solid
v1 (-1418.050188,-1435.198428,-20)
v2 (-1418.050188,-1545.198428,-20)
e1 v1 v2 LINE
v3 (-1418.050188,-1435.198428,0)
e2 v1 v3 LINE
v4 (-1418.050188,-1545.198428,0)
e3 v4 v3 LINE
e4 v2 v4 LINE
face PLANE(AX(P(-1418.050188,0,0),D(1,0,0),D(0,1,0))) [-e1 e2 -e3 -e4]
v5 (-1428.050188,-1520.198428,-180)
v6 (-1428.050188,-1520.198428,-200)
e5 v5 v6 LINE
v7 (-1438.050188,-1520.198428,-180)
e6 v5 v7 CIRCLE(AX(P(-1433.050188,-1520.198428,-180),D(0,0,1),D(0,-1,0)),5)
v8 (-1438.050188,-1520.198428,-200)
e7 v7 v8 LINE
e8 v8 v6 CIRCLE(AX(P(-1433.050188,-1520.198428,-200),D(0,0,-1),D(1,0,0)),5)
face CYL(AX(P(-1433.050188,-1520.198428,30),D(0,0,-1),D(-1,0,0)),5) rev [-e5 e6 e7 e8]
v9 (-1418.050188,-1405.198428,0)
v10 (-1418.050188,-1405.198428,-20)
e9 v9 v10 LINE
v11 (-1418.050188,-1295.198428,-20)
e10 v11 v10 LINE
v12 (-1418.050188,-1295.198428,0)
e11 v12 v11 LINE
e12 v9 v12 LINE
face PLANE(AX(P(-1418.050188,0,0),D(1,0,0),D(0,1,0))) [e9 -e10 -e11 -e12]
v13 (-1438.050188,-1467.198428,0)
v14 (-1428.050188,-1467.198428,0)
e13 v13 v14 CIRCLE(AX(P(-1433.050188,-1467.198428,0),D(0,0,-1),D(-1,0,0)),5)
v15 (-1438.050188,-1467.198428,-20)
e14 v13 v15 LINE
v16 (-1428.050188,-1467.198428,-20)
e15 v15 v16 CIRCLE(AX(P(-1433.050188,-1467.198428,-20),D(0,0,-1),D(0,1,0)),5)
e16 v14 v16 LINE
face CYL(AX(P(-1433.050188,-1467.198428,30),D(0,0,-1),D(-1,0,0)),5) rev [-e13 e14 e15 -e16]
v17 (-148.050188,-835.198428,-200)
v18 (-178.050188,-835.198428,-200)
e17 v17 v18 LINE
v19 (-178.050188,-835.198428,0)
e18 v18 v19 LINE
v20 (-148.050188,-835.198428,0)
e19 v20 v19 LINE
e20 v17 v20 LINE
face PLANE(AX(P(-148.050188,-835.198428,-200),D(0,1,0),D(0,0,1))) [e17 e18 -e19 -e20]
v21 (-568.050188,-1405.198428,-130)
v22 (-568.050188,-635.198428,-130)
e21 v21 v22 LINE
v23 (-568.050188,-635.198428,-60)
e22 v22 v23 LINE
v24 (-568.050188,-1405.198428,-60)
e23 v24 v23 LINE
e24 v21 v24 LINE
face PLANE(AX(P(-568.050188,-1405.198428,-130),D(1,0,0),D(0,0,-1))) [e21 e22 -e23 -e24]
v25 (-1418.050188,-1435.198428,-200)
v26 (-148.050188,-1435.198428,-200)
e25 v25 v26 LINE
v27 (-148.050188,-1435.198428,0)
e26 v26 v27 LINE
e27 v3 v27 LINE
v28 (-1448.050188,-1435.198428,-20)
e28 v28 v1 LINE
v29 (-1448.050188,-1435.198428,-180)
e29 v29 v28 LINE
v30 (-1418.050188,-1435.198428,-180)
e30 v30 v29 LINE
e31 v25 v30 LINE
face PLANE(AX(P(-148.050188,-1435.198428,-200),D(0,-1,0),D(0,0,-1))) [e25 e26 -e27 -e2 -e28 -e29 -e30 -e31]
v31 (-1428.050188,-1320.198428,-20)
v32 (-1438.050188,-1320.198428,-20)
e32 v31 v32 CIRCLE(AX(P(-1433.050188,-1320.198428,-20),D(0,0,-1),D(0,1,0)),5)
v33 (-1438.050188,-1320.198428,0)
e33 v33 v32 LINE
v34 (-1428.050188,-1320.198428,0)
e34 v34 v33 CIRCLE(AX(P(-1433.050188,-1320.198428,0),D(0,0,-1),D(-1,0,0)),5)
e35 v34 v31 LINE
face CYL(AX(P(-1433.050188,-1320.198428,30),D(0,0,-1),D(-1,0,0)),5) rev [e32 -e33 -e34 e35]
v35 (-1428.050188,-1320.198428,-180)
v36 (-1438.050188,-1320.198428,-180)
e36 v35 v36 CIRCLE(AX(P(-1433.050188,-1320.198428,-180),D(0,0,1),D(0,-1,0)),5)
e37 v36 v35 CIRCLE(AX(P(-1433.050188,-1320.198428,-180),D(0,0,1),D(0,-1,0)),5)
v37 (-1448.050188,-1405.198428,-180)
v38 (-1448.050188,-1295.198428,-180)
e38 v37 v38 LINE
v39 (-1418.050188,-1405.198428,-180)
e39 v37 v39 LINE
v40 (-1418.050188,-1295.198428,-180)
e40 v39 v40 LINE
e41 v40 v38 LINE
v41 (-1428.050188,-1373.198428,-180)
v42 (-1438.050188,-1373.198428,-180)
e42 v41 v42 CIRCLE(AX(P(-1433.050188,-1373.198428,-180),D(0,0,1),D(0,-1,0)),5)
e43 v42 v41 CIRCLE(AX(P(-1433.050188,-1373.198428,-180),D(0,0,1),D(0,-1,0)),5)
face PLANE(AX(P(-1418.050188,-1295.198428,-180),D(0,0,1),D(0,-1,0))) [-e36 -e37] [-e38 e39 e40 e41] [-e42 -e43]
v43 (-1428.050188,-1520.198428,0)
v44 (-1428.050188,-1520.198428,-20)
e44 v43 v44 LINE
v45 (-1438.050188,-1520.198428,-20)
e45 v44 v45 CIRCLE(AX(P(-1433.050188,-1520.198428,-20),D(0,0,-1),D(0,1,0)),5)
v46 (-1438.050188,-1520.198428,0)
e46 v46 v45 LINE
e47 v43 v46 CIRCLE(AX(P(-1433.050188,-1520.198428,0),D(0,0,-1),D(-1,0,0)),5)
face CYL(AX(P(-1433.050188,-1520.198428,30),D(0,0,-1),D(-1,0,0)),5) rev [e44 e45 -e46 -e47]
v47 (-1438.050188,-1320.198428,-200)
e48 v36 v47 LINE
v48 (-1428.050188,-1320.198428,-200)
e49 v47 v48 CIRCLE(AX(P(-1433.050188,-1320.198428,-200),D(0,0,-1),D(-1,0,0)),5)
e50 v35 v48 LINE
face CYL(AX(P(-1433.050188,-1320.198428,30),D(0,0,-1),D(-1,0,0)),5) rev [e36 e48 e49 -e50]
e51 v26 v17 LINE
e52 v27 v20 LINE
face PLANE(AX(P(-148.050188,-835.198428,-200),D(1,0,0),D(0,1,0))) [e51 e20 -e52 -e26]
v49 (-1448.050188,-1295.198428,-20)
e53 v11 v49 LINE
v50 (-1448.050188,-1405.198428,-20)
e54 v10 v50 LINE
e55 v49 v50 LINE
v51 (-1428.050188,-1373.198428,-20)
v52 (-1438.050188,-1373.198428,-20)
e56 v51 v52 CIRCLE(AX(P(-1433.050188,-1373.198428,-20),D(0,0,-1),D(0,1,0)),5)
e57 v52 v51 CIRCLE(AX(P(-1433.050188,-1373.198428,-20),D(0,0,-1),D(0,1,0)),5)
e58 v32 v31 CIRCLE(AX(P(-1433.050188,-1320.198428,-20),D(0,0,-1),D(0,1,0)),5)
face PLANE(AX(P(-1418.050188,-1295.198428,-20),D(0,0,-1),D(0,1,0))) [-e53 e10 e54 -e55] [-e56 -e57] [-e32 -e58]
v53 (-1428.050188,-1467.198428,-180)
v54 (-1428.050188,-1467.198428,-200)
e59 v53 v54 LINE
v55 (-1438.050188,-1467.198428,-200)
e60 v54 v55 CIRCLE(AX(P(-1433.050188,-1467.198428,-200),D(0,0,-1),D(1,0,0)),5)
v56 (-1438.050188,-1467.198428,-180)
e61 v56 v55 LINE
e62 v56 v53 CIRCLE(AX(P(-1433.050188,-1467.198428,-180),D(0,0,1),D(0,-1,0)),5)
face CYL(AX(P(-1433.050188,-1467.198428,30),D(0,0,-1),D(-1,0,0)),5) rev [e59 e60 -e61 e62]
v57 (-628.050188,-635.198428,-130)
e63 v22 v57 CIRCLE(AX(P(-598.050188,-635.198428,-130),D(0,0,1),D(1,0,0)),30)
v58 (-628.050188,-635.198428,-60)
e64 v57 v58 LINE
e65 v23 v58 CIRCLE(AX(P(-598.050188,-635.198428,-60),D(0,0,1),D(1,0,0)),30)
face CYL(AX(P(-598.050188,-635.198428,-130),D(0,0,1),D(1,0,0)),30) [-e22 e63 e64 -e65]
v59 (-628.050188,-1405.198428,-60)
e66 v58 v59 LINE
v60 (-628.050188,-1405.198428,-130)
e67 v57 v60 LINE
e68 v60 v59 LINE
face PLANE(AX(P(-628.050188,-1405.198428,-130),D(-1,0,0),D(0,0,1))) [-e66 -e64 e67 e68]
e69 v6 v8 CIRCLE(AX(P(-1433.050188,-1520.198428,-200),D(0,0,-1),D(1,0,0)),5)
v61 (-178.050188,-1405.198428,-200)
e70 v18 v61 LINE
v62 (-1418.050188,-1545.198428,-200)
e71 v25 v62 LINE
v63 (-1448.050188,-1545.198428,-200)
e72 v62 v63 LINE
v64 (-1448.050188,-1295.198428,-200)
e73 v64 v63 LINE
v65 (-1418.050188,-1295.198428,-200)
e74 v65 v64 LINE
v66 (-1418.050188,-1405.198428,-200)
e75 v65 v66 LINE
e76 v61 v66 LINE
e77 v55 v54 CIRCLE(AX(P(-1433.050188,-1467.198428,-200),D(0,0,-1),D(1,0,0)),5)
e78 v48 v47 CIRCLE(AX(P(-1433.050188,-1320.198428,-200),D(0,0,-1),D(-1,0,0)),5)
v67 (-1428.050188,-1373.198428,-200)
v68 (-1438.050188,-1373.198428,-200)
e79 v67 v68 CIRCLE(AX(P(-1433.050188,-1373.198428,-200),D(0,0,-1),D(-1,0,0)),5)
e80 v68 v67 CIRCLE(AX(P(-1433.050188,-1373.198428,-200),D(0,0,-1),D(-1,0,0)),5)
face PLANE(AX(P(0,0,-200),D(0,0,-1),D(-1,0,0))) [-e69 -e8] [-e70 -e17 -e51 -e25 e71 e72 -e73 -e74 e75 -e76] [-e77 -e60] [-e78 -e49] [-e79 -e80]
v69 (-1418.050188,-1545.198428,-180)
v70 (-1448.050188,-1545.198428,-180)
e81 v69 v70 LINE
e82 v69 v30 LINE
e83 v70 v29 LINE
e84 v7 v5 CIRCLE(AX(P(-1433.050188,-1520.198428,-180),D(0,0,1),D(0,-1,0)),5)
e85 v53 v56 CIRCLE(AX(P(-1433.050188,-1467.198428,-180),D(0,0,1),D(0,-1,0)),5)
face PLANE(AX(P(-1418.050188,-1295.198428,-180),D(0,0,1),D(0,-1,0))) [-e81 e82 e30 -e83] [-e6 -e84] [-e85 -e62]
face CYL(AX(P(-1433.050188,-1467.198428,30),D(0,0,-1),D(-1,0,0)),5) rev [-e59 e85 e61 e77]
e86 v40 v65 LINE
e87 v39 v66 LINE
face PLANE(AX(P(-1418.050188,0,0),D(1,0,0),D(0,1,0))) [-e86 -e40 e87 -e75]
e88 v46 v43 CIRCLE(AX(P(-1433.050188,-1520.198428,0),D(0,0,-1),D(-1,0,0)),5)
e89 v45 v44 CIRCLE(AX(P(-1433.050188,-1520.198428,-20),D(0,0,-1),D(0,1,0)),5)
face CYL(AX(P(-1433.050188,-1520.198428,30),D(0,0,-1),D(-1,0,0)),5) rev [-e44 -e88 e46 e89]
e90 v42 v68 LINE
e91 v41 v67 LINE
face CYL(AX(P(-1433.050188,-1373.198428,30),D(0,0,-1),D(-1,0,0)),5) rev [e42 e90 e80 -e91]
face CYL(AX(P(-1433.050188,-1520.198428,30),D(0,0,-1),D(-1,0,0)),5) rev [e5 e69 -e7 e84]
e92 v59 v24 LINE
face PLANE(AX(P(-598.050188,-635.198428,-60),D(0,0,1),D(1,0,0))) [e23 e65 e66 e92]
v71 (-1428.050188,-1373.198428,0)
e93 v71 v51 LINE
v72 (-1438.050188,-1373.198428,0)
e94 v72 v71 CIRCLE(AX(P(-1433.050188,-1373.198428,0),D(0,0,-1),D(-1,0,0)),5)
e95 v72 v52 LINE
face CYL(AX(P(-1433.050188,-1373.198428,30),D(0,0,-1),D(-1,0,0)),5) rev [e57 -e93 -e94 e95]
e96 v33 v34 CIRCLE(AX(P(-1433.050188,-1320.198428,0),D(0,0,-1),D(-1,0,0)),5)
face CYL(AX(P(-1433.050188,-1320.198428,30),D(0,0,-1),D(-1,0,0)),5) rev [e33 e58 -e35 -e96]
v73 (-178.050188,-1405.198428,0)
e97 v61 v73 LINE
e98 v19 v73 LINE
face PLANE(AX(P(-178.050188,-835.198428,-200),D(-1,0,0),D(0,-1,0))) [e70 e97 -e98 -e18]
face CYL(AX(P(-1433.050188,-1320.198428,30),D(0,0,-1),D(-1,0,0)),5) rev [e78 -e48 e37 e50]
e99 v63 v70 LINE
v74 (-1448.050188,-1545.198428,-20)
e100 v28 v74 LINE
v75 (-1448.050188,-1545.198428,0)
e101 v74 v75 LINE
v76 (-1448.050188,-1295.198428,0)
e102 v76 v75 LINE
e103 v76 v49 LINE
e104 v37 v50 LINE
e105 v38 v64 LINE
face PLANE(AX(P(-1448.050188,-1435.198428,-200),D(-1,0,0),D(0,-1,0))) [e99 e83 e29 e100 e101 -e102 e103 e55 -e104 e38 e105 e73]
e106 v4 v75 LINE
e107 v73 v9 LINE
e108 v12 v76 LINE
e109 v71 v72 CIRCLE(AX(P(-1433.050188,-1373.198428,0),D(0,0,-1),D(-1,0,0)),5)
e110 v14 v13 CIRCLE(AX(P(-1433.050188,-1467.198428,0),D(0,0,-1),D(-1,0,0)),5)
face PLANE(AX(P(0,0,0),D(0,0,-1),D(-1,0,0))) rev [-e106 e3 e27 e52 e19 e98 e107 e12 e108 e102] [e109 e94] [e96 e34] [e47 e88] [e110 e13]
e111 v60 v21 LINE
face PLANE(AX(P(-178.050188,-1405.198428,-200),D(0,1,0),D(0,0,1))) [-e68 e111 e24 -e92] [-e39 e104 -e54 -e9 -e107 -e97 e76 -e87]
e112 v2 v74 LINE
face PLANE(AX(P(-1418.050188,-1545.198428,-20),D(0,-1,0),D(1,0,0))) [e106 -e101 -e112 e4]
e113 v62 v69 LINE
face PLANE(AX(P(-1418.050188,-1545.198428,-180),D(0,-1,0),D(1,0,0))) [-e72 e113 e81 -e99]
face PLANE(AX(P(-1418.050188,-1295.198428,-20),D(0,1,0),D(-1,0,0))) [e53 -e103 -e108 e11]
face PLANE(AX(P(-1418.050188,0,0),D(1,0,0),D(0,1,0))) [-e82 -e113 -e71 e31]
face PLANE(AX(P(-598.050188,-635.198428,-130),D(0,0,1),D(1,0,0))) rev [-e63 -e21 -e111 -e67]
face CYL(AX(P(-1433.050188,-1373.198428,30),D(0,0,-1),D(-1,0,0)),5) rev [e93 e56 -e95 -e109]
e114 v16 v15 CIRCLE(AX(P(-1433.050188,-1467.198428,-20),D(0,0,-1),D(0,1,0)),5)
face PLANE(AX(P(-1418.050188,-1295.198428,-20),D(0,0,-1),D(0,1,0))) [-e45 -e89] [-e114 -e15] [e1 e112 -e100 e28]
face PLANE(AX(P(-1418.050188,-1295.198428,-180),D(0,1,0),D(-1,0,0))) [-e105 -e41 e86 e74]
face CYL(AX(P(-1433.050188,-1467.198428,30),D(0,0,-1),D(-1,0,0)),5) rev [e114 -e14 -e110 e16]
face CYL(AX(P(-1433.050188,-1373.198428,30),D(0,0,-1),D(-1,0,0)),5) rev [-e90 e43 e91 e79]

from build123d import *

# Parameters (mm, degrees)
BOSS_EXTRUDE1_DEPTH = 200
SKETCH4_W           = 20
SKETCH4_H           = 250
BOSS_EXTRUDE2_DEPTH = 30
SKETCH5_R           = 5
CUT_EXTRUDE1_DEPTH  = 230
BOSS_EXTRUDE5_START = -60
BOSS_EXTRUDE5_DEPTH = 70


with BuildPart() as part:
    # Sketch2 → Boss-Extrude1 (new body)
    with BuildSketch(Plane.XY):
        Polygon((-148.050188004, -835.198427503), (-178.050188004, -835.198427503), (-178.050188004, -1405.198427503), (-1448.050188004, -1405.198427503), (-1448.050188004, -1435.198427503), (-148.050188004, -1435.198427503), align=None)
    extrude(amount=-BOSS_EXTRUDE1_DEPTH)

    # Sketch4 → Boss-Extrude2 (add)
    with BuildSketch(Plane.ZY.offset(1448.050188004)):
        with Locations((-190, -1420.198427503)):
            Rectangle(SKETCH4_W, SKETCH4_H)
        with Locations((-10, -1420.198427503)):
            Rectangle(SKETCH4_W, SKETCH4_H)
    extrude(amount=-BOSS_EXTRUDE2_DEPTH)

    # Sketch5 → Cut-Extrude1 (cut)
    with BuildSketch(Plane(origin=(0, 0, -200), x_dir=(-1, 0, 0), z_dir=(0, 0, -1))):
        with Locations((1433.050188004, -1320.198427503)):
            Circle(SKETCH5_R)
        with Locations((1433.050188004, -1373.198427503)):
            Circle(SKETCH5_R)
        with Locations((1433.050188004, -1520.198427503)):
            Circle(SKETCH5_R)
        with Locations((1433.050188004, -1467.198427503)):
            Circle(SKETCH5_R)
    extrude(amount=-CUT_EXTRUDE1_DEPTH, mode=Mode.SUBTRACT)

    # Sketch9 → Boss-Extrude5 (add)
    with BuildSketch(Plane.XY.offset(BOSS_EXTRUDE5_START)):
        with BuildLine():
            Line((-568.050188004, -1405.198427503), (-628.050188004, -1405.198427503))
            Line((-628.050188004, -1405.198427503), (-628.050188004, -635.198427503))
            ThreePointArc((-628.050188004, -635.198427503), (-598.050188004, -605.198427503), (-568.050188004, -635.198427503))
            Line((-568.050188004, -635.198427503), (-568.050188004, -1405.198427503))
        make_face()
    extrude(amount=-BOSS_EXTRUDE5_DEPTH)


solid = part.part
